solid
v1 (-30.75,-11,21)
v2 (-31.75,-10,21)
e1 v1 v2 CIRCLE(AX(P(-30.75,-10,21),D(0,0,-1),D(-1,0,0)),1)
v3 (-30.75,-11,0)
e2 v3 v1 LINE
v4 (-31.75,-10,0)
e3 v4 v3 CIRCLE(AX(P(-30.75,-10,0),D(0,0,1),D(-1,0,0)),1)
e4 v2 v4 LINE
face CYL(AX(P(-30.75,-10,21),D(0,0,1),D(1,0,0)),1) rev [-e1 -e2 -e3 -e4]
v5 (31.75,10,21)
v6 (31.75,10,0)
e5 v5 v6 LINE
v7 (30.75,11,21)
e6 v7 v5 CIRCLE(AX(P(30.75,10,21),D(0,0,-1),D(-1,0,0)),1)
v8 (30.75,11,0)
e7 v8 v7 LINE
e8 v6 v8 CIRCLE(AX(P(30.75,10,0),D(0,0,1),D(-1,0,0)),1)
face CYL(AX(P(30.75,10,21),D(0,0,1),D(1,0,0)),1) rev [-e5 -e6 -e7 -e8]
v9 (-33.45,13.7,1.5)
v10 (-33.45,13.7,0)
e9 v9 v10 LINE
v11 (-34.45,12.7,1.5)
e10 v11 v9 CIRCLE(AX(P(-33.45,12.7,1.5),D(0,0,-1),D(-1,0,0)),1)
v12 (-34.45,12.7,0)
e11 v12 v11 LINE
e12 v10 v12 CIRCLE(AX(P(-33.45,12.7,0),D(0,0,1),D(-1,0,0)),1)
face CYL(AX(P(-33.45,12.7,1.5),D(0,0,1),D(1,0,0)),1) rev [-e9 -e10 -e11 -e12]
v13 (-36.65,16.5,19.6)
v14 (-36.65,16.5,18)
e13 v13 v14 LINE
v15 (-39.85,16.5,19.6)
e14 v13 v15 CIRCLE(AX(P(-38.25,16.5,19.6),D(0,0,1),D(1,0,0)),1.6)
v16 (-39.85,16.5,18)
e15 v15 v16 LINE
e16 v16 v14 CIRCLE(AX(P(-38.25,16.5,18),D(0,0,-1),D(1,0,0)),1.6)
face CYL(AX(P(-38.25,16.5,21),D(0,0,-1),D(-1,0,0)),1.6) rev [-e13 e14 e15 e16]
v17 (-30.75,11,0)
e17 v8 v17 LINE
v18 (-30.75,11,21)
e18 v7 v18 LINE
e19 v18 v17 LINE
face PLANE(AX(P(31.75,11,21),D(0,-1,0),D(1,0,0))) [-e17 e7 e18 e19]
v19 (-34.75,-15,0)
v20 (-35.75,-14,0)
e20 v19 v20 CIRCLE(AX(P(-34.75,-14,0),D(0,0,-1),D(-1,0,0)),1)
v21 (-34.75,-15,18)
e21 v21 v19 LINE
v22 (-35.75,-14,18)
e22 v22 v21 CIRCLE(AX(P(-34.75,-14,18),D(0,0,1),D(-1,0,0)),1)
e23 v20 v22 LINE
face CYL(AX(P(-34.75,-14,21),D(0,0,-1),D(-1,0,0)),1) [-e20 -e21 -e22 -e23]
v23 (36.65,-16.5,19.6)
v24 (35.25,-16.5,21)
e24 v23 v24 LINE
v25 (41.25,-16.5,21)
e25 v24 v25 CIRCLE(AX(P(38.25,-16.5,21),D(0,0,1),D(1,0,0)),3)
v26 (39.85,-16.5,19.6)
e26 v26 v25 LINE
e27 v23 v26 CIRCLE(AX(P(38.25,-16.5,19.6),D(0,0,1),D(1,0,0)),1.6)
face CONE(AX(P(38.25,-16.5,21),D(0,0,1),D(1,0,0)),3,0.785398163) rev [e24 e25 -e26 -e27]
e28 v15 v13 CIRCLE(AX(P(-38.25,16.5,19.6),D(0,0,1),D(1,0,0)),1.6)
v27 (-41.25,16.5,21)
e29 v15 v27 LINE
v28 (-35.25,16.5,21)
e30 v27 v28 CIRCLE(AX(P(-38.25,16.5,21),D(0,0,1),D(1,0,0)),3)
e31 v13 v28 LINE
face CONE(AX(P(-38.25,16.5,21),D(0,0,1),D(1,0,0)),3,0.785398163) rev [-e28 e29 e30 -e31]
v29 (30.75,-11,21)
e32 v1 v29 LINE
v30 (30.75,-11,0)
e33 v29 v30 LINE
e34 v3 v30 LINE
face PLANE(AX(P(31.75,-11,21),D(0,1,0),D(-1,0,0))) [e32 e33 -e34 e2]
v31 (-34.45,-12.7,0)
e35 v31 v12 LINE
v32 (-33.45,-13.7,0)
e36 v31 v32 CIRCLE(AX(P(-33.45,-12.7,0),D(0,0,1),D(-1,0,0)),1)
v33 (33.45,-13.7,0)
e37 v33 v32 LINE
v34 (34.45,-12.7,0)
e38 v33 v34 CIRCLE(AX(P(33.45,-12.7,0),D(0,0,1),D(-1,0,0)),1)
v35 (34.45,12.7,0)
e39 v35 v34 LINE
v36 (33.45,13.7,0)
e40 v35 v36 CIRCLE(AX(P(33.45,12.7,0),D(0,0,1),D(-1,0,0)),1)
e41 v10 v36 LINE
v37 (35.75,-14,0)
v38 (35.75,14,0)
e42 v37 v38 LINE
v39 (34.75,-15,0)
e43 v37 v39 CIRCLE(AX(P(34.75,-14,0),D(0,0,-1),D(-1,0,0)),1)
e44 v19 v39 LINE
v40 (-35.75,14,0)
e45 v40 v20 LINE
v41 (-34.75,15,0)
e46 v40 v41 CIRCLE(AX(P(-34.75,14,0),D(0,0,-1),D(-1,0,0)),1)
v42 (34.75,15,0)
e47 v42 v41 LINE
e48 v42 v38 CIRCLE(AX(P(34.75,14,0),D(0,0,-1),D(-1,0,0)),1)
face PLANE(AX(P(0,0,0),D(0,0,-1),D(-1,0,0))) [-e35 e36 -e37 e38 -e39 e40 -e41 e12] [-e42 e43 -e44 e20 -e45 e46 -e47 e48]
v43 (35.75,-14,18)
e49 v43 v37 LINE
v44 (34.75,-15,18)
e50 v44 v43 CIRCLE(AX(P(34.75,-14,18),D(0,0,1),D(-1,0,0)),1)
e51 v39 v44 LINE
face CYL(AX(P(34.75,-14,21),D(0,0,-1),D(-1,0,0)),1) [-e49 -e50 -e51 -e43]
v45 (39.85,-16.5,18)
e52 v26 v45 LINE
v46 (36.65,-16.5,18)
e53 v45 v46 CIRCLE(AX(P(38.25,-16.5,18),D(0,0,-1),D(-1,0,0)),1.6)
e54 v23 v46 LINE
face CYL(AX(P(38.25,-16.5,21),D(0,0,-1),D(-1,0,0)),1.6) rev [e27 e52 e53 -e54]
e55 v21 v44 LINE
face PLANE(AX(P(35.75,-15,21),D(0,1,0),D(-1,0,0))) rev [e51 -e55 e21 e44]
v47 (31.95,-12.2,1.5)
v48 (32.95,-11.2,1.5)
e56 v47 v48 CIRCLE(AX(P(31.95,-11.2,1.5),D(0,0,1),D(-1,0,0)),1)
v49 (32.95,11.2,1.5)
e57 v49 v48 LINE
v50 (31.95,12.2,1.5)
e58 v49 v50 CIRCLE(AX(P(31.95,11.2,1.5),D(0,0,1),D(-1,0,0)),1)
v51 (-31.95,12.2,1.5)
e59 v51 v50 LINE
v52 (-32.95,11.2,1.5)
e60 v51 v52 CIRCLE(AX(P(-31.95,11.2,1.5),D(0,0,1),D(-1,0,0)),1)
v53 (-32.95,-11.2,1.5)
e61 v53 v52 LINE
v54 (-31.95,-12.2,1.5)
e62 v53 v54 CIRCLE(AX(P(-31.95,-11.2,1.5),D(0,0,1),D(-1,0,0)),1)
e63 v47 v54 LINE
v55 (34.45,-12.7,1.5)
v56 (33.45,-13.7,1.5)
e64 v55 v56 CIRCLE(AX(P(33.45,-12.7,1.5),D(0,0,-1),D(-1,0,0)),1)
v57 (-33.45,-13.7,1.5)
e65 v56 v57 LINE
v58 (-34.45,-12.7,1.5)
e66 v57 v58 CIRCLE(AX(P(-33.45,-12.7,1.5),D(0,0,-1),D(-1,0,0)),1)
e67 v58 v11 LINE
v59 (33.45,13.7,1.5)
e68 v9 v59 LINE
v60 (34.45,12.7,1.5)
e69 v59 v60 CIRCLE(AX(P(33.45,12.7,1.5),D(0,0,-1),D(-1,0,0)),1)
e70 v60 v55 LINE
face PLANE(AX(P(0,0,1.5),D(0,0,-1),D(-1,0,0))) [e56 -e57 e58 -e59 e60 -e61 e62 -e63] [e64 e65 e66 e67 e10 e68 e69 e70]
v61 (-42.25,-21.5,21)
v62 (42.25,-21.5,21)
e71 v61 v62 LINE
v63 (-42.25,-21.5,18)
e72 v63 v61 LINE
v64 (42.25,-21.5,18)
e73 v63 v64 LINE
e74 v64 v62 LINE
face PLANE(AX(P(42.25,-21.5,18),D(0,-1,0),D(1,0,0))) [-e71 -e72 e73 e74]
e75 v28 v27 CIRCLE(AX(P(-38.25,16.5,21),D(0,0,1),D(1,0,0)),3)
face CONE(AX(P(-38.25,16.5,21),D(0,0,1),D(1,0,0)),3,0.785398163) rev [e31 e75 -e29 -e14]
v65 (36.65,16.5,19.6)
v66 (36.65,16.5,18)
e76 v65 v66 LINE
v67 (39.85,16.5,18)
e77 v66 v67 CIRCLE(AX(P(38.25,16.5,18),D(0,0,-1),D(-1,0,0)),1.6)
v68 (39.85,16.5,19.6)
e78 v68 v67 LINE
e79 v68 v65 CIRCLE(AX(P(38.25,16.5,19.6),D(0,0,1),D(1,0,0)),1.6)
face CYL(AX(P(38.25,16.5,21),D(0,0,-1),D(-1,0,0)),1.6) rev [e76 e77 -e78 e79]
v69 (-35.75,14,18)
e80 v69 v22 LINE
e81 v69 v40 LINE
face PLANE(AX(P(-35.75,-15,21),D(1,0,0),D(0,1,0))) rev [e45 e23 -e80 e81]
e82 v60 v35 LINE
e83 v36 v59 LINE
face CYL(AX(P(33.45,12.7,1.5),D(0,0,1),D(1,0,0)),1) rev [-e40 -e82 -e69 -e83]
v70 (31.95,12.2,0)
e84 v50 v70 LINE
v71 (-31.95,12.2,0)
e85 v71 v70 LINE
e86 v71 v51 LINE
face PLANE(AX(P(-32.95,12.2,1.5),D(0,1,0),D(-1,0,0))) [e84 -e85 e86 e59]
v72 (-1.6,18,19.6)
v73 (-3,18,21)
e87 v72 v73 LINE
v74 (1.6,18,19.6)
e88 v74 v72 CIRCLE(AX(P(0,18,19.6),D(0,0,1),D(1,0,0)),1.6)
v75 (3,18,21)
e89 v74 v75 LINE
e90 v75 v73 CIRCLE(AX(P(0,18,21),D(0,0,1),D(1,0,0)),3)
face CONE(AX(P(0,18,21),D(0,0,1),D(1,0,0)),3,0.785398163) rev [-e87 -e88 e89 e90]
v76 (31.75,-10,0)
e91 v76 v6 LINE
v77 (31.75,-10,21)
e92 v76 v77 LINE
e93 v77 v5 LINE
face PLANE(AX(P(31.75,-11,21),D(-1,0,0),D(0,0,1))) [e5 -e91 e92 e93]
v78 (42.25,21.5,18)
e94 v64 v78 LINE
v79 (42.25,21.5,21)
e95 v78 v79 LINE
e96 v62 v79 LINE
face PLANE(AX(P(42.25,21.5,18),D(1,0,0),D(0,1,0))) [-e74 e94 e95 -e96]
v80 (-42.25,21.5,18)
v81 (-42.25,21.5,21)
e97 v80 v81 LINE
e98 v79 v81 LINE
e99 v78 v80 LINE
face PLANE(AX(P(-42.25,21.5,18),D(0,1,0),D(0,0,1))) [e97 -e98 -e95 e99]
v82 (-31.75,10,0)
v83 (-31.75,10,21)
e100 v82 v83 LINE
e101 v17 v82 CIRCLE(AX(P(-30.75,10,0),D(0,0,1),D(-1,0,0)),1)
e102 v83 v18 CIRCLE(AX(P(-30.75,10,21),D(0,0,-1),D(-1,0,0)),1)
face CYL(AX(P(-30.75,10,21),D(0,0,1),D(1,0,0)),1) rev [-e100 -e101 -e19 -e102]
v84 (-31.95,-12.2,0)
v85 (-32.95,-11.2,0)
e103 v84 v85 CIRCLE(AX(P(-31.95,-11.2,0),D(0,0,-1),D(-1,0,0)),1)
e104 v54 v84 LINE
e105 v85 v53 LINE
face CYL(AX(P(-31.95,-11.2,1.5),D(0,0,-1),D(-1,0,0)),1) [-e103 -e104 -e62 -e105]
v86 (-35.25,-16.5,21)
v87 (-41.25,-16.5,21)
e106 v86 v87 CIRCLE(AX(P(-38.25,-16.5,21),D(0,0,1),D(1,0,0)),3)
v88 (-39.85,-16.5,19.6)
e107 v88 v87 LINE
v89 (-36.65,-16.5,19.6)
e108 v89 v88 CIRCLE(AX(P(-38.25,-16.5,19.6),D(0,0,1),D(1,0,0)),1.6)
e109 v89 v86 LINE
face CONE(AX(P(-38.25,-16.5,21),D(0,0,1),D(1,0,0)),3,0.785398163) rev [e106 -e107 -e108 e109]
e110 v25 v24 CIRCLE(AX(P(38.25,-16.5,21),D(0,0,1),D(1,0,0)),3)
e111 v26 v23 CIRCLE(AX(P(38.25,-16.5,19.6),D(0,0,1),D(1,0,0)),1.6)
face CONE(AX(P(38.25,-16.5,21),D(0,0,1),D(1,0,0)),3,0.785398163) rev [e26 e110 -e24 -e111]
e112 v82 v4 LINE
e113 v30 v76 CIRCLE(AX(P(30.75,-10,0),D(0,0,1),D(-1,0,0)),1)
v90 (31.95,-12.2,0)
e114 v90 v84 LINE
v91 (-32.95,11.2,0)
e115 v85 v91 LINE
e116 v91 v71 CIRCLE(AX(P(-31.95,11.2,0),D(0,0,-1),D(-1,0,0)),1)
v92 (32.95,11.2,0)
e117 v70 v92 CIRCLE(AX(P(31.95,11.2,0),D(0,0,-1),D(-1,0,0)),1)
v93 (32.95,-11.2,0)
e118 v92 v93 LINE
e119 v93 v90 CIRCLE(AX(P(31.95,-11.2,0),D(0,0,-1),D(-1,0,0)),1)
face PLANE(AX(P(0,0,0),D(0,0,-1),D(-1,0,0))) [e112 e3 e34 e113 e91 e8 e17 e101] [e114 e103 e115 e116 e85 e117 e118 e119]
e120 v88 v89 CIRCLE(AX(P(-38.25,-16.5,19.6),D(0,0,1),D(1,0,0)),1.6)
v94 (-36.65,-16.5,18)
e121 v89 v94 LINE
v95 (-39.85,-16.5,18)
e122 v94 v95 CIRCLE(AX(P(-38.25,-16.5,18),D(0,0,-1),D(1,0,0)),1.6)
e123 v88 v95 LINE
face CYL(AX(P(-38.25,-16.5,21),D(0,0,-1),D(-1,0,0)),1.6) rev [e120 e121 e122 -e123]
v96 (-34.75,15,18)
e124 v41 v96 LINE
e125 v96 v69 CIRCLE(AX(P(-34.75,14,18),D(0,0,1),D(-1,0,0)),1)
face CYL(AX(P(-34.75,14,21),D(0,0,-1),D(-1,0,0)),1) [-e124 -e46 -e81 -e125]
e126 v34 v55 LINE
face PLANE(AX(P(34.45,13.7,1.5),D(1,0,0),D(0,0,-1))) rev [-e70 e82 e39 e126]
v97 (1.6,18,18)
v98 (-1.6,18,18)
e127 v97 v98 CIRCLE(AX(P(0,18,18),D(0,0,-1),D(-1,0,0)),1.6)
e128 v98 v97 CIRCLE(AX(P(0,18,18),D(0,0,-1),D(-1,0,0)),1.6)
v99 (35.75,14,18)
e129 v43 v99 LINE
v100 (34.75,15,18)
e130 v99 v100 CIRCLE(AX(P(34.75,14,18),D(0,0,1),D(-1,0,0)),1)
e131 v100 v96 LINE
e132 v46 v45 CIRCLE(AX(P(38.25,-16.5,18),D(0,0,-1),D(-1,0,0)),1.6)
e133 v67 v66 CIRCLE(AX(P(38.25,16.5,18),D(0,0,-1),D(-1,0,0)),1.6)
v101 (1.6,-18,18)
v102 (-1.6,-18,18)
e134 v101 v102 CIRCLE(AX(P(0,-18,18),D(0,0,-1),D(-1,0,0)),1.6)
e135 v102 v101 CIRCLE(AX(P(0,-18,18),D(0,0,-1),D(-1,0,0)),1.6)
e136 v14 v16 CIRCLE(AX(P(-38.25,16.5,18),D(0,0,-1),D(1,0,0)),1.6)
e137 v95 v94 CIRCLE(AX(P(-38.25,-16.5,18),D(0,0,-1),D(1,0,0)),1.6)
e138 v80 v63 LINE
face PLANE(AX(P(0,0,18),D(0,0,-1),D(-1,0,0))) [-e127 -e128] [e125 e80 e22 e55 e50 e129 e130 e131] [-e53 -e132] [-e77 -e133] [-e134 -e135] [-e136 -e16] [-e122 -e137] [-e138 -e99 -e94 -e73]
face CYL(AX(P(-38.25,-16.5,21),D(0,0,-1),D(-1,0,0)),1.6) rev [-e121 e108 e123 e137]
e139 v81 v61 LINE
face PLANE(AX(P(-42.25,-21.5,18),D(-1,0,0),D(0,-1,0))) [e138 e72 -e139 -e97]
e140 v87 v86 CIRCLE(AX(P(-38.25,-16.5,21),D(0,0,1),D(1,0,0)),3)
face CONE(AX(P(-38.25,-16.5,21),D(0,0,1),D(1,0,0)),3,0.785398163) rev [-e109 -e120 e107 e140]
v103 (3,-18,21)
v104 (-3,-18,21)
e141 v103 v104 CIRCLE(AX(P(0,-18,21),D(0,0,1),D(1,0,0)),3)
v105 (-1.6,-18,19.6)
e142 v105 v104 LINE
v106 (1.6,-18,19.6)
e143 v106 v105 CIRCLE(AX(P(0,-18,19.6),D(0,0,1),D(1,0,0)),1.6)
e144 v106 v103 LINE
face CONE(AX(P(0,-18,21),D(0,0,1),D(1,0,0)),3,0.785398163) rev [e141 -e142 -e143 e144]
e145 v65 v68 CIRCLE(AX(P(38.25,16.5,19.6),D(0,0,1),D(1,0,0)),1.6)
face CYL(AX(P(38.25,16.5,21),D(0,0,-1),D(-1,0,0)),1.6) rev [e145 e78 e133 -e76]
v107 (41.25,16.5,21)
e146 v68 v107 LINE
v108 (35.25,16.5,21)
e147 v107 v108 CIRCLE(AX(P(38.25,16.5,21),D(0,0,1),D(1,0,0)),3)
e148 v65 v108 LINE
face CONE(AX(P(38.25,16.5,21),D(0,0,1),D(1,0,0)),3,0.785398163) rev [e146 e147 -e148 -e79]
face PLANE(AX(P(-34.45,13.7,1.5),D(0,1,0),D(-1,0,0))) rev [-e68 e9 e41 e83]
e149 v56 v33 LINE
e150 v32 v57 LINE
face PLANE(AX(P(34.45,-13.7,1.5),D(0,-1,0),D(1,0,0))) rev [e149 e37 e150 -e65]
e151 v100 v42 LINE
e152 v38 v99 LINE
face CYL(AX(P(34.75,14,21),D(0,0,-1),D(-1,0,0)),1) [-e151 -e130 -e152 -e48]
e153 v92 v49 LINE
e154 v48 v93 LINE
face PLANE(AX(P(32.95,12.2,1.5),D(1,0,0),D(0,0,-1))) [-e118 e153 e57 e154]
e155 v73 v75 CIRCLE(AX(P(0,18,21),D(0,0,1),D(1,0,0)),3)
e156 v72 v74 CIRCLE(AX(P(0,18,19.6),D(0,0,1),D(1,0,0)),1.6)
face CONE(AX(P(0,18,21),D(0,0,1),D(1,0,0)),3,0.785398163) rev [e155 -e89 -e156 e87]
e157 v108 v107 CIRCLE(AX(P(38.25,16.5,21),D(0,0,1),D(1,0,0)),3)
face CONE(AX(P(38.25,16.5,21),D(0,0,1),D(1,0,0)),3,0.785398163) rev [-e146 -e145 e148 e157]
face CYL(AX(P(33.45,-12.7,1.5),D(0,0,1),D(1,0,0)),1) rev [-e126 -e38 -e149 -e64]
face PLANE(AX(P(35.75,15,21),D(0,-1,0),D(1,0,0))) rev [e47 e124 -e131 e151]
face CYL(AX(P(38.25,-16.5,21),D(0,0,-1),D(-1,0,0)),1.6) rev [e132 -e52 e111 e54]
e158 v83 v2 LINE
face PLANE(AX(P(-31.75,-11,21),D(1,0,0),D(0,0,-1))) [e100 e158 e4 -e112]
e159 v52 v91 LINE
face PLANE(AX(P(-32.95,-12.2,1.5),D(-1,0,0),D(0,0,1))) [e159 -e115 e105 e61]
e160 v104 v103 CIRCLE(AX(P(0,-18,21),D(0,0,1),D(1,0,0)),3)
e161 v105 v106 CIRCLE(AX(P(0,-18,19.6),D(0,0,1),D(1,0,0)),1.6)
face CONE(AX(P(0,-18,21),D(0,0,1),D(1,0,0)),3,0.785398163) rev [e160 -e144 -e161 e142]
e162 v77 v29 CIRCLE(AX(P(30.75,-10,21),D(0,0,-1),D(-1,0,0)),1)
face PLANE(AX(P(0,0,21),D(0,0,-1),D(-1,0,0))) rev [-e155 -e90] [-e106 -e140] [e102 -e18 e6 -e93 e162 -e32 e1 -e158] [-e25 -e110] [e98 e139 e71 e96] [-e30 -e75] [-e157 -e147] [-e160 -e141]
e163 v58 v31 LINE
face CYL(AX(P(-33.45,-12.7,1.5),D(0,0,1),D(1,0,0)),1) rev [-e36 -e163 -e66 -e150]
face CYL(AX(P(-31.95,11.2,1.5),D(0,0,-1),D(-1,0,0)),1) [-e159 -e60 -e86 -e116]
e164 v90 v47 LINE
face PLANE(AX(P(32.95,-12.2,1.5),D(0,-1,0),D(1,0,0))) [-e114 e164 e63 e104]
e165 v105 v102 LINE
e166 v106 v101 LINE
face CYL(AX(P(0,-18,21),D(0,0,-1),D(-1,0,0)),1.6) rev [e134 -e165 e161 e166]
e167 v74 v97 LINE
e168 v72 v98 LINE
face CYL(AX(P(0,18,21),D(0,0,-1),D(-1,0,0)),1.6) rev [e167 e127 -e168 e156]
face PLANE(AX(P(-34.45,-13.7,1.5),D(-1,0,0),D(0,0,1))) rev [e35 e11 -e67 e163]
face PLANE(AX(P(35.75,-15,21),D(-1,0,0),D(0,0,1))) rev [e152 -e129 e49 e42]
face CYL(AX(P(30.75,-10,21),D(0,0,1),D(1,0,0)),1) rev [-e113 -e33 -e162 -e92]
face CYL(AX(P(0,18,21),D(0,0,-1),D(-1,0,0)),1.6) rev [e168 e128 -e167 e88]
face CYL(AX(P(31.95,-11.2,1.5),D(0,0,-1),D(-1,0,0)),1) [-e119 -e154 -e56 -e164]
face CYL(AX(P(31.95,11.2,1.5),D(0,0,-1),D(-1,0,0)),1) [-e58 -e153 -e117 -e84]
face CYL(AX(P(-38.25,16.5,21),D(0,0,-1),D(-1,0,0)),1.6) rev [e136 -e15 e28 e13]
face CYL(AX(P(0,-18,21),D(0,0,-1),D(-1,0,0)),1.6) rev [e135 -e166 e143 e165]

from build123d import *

# Parameters (mm, degrees)
SKETCH1_W                                         = 71.5
SKETCH1_H                                         = 30
SKETCH1_W_2                                       = 63.5
SKETCH1_H_2                                       = 22
BOSS_EXTRUDE1_DEPTH                               = 21
SKETCH2_W                                         = 71.5
SKETCH2_H                                         = 30
BOSS_EXTRUDE2_DEPTH                               = 3
SKETCH3_W                                         = 68.9
SKETCH3_H                                         = 27.4
SKETCH3_W_2                                       = 65.9
SKETCH3_H_2                                       = 24.4
CUT_EXTRUDE1_DEPTH                                = 1.5
SKETCH4_R                                         = 1.6
CUT_EXTRUDE2_DEPTH                                = 3
PILOT_HOLE_SIZE_PER_CROSS_FOR_HALF_CO_D           = 3.2
PILOT_HOLE_SIZE_PER_CROSS_FOR_HALF_CO_DEPTH       = 6.1
PILOT_HOLE_SIZE_PER_CROSS_FOR_HALF_CO_CSINK_D     = 6
PILOT_HOLE_SIZE_PER_CROSS_FOR_HALF_CO_CSINK_ANGLE = 90
PILOT_HOLE_SIZE_PER_CROSS_FOR_HALF_CO_TIP         = 0.96137699
FILLET1_R                                         = 1
FILLET2_R                                         = 1


with BuildPart() as part:
    # Sketch1 → Boss-Extrude1 (new body)
    with BuildSketch(Plane.XY):
        Rectangle(SKETCH1_W, SKETCH1_H)
        Rectangle(SKETCH1_W_2, SKETCH1_H_2, mode=Mode.SUBTRACT)
    extrude(amount=BOSS_EXTRUDE1_DEPTH)

    # Sketch2 → Boss-Extrude2 (add)
    with BuildSketch(Plane.XY.offset(21)):
        Polygon((42.25, 15), (42.25, -15), (42.25, -21.5), (-42.25, -21.5), (-42.25, -15), (-42.25, 15), (-42.25, 21.5), (42.25, 21.5), align=None)
        Rectangle(SKETCH2_W, SKETCH2_H, mode=Mode.SUBTRACT)
    extrude(amount=-BOSS_EXTRUDE2_DEPTH)

    # Sketch3 → Cut-Extrude1 (cut)
    with BuildSketch(Plane(origin=(0, 0, 0), x_dir=(-1, 0, 0), z_dir=(0, 0, -1))):
        Rectangle(SKETCH3_W, SKETCH3_H)
        Rectangle(SKETCH3_W_2, SKETCH3_H_2, mode=Mode.SUBTRACT)
    extrude(amount=-CUT_EXTRUDE1_DEPTH, mode=Mode.SUBTRACT)

    # Sketch4 → Cut-Extrude2 (cut)
    with BuildSketch(Plane(origin=(0, 0, 18), x_dir=(-1, 0, 0), z_dir=(0, 0, -1))):
        with Locations((-38.25, 16.5)):
            Circle(SKETCH4_R)
        with Locations((-38.25, -16.5)):
            Circle(SKETCH4_R)
        with Locations(Location((38.25, -16.5, 0), (0, 0, 180))):
            Circle(SKETCH4_R)
        with Locations(Location((38.25, 16.5, 0), (0, 0, 180))):
            Circle(SKETCH4_R)
        with Locations((0, -18)):
            Circle(SKETCH4_R)
        with Locations((0, 18)):
            Circle(SKETCH4_R)
    extrude(amount=-CUT_EXTRUDE2_DEPTH, mode=Mode.SUBTRACT)

    # Pilot hole size (% per cross) for half-countersunk wood screw, type 1
    with Locations(Plane.XY.offset(21)):
        with Locations((-38.25, 16.5), (-38.25, -16.5), (38.25, 16.5), (38.25, -16.5), (0, -18), (0, 18)):
            CounterSinkHole(PILOT_HOLE_SIZE_PER_CROSS_FOR_HALF_CO_D / 2, PILOT_HOLE_SIZE_PER_CROSS_FOR_HALF_CO_CSINK_D / 2, depth=PILOT_HOLE_SIZE_PER_CROSS_FOR_HALF_CO_DEPTH, counter_sink_angle=PILOT_HOLE_SIZE_PER_CROSS_FOR_HALF_CO_CSINK_ANGLE)
            with Locations((0, 0, -(PILOT_HOLE_SIZE_PER_CROSS_FOR_HALF_CO_DEPTH + PILOT_HOLE_SIZE_PER_CROSS_FOR_HALF_CO_TIP / 2))):  # 118° drill point
                Cone(0, PILOT_HOLE_SIZE_PER_CROSS_FOR_HALF_CO_D / 2, PILOT_HOLE_SIZE_PER_CROSS_FOR_HALF_CO_TIP, mode=Mode.SUBTRACT)

    # Fillet1
    fillet1_edges = [part.edges().sort_by_distance(p)[0] for p in [
        (-31.75, 11, 10.5),
        (-31.75, -11, 10.5),
        (31.75, -11, 10.5),
        (31.75, 11, 10.5),
        (34.45, 13.7, 0.75),
        (-34.45, 13.7, 0.75),
        (-34.45, -13.7, 0.75),
        (34.45, -13.7, 0.75),
        (32.95, -12.2, 0.75),
        (32.95, 12.2, 0.75),
        (-32.95, 12.2, 0.75),
        (-32.95, -12.2, 0.75),
    ]]
    fillet(fillet1_edges, radius=FILLET1_R)

    # Fillet2
    fillet2_edges = [part.edges().sort_by_distance(p)[0] for p in [
        (-35.75, -15, 9),
        (-35.75, 15, 9),
        (35.75, 15, 9),
        (35.75, -15, 9),
    ]]
    fillet(fillet2_edges, radius=FILLET2_R)


solid = part.part
